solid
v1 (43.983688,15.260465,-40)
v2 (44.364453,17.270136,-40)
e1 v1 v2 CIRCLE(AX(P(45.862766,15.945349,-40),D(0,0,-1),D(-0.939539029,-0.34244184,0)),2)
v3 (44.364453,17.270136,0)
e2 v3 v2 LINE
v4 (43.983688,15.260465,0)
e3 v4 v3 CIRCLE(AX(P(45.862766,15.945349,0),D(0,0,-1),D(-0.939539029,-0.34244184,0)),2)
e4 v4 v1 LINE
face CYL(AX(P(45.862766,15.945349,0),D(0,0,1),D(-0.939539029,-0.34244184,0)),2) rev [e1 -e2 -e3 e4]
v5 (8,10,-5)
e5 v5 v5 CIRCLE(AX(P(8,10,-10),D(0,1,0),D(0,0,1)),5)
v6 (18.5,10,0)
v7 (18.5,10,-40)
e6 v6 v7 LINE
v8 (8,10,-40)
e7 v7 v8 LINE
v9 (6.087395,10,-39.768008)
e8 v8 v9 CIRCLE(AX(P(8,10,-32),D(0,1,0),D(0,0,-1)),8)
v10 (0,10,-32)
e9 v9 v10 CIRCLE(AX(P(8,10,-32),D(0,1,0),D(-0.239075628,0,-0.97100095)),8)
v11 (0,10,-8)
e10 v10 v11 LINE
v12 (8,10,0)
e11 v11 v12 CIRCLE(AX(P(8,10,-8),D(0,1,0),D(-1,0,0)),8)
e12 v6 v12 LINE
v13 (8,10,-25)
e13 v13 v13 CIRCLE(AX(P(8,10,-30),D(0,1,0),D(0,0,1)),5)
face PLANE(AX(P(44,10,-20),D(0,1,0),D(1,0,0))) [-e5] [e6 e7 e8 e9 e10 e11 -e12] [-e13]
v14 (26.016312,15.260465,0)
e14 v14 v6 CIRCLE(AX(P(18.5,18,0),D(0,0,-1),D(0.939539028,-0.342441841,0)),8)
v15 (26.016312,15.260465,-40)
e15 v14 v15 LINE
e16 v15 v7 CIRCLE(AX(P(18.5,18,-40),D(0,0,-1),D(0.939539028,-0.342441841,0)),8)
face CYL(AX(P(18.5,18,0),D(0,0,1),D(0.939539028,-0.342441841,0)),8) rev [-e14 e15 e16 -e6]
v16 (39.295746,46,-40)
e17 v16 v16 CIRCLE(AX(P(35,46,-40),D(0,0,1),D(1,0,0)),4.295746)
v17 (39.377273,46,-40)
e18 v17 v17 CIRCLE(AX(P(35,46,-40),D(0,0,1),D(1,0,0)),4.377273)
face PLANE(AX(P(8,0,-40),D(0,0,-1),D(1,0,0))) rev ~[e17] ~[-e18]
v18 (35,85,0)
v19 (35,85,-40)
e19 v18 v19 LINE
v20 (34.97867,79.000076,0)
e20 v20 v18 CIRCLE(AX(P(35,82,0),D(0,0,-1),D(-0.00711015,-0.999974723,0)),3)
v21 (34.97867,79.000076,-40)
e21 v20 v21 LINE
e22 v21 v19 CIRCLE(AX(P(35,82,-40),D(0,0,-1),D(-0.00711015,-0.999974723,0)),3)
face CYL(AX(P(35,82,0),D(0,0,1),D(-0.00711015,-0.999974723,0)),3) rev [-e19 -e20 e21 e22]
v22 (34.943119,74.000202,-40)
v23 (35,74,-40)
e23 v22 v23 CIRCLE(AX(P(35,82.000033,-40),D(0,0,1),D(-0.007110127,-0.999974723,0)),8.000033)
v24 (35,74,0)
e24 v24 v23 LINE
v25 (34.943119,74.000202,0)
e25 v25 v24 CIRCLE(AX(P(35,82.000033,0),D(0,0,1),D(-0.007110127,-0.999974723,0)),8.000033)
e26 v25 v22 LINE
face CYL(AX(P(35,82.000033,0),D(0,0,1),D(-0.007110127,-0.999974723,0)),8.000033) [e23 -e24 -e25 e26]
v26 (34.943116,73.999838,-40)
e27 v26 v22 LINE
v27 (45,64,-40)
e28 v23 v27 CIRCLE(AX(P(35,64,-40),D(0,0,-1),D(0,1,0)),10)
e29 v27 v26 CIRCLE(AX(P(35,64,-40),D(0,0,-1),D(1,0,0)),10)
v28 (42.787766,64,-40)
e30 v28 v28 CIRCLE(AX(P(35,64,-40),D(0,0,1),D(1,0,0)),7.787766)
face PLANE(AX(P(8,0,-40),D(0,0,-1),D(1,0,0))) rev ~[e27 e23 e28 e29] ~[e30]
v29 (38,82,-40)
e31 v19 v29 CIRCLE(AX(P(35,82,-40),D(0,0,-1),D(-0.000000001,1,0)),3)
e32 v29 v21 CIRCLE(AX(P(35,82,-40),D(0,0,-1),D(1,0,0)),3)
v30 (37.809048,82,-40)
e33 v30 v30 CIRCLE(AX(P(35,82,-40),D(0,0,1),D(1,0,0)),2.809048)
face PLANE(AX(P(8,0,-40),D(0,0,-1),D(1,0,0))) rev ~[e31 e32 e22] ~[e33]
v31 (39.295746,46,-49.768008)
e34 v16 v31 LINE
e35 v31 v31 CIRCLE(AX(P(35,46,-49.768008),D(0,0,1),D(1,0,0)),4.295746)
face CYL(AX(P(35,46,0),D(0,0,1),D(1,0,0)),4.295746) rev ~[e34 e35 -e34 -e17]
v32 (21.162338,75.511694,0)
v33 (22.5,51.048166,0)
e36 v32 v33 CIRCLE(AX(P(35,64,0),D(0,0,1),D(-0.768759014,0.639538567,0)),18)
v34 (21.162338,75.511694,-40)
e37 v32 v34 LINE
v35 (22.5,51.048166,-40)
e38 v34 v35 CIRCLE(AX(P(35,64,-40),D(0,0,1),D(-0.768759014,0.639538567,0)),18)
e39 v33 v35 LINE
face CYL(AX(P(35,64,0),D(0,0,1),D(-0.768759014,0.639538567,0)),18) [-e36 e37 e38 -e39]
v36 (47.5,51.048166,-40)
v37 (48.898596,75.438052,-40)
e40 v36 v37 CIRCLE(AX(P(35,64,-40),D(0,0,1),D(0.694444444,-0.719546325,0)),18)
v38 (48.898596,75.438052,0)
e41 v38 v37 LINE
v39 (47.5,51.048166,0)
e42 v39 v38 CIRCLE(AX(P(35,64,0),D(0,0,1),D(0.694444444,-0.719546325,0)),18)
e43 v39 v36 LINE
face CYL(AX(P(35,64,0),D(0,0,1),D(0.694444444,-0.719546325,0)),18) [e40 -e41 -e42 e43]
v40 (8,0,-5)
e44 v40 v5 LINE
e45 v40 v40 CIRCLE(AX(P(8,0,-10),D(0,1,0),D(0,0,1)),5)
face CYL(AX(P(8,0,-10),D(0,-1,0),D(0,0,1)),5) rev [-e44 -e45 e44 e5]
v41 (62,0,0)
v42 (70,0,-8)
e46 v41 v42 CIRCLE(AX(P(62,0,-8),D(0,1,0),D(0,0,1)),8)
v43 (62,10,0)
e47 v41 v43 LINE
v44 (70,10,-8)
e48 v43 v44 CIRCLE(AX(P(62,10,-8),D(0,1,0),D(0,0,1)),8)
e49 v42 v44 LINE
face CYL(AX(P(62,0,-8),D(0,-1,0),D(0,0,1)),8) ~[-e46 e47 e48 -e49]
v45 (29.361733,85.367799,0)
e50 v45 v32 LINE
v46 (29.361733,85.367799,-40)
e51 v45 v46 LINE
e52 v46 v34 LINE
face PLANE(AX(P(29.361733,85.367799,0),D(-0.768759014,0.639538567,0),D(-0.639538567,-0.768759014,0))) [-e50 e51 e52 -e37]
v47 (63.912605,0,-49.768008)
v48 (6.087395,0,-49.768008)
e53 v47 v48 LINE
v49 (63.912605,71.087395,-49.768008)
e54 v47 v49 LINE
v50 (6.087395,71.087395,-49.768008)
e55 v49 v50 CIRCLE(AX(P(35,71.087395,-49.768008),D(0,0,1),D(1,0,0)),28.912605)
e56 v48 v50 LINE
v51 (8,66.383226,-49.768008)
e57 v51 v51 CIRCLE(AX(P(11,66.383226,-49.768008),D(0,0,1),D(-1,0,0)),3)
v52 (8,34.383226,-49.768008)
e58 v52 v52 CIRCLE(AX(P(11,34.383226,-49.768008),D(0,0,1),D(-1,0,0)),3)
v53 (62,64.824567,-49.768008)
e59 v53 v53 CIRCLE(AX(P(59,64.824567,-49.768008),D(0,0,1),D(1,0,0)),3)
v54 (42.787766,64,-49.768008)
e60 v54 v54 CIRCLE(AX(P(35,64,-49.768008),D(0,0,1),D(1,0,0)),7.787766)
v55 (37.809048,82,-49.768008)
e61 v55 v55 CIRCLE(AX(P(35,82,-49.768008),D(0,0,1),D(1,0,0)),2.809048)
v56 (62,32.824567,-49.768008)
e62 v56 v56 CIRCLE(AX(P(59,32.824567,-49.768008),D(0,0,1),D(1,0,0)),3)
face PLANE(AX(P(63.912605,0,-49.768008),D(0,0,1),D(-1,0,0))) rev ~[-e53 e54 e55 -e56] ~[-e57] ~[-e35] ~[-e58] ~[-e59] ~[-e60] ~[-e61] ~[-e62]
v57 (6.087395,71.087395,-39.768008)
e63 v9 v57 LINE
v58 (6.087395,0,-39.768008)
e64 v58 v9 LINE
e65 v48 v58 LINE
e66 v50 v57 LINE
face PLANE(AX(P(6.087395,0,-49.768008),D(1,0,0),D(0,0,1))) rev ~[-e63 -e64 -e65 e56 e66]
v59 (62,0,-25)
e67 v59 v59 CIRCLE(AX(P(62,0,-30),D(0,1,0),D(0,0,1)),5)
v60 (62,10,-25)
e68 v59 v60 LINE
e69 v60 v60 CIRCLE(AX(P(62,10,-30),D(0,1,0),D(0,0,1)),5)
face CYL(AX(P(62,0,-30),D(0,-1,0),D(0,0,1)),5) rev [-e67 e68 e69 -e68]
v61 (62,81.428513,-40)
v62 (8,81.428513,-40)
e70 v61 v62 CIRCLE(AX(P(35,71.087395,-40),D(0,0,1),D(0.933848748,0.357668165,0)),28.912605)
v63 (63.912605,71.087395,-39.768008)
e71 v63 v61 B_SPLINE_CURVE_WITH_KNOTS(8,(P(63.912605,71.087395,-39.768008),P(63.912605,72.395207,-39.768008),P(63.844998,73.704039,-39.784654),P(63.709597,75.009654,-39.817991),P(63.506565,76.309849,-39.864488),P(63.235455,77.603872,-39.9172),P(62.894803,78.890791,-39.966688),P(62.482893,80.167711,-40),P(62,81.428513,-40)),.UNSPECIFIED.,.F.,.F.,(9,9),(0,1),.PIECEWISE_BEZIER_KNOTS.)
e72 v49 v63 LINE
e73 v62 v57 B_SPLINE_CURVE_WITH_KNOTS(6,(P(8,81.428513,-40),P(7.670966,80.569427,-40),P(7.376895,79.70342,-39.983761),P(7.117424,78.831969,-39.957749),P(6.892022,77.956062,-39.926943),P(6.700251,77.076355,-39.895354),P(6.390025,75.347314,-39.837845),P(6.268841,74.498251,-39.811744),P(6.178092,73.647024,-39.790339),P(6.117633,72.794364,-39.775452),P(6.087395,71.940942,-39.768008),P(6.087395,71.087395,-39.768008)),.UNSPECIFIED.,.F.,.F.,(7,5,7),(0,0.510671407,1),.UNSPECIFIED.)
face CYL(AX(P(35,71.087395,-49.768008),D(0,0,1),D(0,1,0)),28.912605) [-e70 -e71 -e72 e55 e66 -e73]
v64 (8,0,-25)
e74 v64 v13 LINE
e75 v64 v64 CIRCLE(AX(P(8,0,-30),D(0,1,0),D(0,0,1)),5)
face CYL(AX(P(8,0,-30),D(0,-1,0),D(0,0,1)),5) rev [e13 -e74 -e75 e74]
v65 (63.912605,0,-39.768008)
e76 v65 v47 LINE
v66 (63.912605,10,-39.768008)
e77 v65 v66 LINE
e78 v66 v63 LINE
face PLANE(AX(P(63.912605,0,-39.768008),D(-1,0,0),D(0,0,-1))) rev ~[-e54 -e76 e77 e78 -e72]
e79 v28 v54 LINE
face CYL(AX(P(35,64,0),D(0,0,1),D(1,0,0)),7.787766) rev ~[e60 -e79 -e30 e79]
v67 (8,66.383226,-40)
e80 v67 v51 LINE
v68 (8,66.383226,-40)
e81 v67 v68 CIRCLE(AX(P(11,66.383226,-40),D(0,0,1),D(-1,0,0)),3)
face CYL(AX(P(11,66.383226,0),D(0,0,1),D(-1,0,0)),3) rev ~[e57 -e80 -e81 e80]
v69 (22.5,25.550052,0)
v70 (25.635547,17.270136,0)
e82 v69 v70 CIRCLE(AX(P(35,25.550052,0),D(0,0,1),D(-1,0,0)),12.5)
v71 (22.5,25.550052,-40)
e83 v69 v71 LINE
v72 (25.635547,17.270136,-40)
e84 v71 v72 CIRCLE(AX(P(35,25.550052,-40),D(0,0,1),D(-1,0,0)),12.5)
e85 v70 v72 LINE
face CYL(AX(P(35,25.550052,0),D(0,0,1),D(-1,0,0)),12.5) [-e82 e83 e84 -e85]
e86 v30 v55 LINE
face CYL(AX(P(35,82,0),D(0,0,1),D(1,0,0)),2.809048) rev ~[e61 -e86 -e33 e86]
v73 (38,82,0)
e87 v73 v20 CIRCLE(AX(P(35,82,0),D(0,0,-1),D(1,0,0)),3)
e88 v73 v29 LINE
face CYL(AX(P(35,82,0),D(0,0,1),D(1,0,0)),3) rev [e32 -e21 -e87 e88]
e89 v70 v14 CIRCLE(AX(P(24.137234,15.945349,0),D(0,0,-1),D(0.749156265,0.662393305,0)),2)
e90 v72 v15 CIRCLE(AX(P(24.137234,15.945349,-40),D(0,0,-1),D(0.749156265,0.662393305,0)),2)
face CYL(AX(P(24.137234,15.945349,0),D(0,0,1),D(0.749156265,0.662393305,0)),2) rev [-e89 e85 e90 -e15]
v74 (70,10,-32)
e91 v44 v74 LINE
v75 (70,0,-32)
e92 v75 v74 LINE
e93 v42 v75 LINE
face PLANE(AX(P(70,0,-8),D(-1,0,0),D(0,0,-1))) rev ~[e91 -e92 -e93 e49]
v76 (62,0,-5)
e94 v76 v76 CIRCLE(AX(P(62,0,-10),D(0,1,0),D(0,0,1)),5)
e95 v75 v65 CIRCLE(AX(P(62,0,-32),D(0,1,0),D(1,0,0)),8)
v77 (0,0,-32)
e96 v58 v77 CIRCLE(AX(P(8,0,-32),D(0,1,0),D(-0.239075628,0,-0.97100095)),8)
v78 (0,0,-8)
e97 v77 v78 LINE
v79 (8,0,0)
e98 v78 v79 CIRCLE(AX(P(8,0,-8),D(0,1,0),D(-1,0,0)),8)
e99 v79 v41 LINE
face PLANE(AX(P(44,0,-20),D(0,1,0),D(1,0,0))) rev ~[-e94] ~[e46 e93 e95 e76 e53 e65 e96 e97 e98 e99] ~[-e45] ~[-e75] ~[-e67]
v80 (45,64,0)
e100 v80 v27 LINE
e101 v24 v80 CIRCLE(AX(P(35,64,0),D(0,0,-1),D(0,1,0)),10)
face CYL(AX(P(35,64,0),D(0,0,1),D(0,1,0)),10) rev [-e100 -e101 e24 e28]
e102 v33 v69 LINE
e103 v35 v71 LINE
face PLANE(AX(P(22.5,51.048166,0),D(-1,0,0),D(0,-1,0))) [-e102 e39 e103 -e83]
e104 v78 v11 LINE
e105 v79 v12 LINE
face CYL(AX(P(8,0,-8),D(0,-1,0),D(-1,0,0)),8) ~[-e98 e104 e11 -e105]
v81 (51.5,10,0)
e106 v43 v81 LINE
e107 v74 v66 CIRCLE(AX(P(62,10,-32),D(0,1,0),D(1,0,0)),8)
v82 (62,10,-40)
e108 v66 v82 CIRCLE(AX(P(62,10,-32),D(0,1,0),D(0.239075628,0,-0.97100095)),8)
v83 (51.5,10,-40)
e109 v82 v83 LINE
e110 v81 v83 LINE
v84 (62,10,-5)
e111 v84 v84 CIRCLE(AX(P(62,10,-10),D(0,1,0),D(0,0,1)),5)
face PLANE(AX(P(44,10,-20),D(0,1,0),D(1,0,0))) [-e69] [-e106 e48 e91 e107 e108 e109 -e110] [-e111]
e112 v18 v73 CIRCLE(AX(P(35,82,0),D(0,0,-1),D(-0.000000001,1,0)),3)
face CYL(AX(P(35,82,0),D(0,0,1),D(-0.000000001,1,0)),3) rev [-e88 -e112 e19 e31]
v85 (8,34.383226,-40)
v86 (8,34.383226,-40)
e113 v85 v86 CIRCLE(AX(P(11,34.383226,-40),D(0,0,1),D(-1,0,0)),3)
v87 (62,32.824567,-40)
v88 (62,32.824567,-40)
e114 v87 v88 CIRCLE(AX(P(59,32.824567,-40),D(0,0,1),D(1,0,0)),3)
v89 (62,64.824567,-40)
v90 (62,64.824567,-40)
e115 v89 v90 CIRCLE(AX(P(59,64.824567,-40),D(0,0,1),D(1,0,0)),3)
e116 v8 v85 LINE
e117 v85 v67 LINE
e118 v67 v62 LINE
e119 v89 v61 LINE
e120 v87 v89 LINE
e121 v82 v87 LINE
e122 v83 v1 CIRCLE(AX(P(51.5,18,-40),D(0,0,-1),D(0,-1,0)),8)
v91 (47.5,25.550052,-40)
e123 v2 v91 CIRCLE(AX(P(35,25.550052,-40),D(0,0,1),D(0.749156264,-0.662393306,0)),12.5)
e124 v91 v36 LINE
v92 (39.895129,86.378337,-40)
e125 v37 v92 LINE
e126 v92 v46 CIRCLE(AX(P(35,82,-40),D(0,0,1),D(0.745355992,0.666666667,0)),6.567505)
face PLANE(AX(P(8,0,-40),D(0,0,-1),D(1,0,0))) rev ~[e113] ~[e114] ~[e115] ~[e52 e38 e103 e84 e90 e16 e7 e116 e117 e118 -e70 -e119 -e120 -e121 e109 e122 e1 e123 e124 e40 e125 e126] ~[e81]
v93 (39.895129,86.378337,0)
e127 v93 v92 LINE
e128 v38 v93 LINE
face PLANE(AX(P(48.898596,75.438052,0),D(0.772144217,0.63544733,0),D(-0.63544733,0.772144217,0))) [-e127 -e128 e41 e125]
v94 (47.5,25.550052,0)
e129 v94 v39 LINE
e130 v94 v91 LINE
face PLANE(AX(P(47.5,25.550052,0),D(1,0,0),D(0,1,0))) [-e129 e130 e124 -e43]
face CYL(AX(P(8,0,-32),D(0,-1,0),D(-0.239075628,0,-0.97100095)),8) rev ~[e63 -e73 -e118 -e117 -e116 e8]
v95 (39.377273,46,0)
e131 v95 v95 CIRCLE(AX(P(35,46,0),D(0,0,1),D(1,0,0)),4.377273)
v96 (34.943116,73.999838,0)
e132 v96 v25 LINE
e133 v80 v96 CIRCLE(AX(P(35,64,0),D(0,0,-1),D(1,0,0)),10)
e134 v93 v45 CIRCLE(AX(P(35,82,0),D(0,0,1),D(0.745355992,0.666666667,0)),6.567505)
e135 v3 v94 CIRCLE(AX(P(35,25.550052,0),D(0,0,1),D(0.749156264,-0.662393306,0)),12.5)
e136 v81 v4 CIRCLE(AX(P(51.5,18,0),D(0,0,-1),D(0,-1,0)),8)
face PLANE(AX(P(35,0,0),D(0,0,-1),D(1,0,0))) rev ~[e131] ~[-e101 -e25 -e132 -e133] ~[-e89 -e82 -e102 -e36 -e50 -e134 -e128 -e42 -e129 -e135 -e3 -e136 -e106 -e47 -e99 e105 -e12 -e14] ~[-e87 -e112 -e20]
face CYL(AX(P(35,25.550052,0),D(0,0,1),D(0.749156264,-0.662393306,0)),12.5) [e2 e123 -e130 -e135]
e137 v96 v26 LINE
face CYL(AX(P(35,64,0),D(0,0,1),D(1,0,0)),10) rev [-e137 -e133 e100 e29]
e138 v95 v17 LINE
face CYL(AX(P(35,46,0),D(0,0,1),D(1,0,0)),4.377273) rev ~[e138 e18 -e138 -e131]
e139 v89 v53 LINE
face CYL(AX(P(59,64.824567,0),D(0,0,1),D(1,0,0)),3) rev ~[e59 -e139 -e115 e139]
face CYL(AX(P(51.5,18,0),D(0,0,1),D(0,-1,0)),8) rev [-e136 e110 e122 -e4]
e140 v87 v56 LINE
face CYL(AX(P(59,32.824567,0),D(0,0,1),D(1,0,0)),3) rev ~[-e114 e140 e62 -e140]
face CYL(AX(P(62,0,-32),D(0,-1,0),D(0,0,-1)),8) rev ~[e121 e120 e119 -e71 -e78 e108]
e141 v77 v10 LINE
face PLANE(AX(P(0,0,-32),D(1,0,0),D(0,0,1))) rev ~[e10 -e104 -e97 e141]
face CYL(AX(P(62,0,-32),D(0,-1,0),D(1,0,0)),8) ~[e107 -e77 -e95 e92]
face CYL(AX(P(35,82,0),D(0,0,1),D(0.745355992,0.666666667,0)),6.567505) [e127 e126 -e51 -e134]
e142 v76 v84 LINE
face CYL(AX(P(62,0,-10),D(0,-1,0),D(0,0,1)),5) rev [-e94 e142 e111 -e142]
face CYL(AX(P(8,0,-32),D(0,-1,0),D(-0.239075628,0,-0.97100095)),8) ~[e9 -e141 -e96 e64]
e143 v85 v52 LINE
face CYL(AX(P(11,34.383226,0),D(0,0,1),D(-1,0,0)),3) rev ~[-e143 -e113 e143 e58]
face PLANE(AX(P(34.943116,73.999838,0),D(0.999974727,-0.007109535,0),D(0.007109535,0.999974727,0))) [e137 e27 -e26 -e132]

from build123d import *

# Parameters (mm, degrees)
BASE_PLATE_AND_COLUMN_SKETCH_R = 5
BASE_PLATE_AND_COLUMN_SKETCH_W = 18
BASE_PLATE_AND_COLUMN_SKETCH_H = 40
BASE_PLATE_DEPTH               = 10
FRONT_PROFILE_SKETCH_R         = 4.377272593
FRONT_PROFILE_BOSS_40MM_DEPTH  = 40
UPRIGHT_COLUMN_100MM_DEPTH     = 100
COLUMN_EDGE_FILLETS_RADIUS     = 28.912605022
COLUMN_EDGE_FILLETS_LENGTH     = 10
SKETCH2_6_R                    = 4.295746386
SKETCH2_6_R_2                  = 7.787765557
SKETCH2_6_R_3                  = 2.809047726
THROUGH_CUT_A_DEPTH            = 100
SKETCH2_7_R                    = 3
THROUGH_CUT_B_DEPTH            = 100


with BuildPart() as part:
    # Base Plate and Column Sketch → Base Plate (new body)
    # profile 1 of 4: a face of its own
    with BuildSketch(Plane(origin=(0, 0, 0), x_dir=(1, 0, 0), z_dir=(0, 1, 0))):
        with BuildLine():
            Line((53, 40), (53, 0))
            Line((53, 0), (62, 0))
            ThreePointArc((62, 0), (67.656854249, 2.343145751), (70, 8))
            Line((70, 8), (70, 32))
            ThreePointArc((70, 32), (68.296857954, 36.934529351), (63.912605022, 39.768007597))
            ThreePointArc((63.912605022, 39.768007597), (62.963311793, 39.941790125), (62, 40))
            Line((62, 40), (53, 40))
        make_face()
        with Locations(Location((62, 10, 0), (0, 0, 270))):
            Circle(BASE_PLATE_AND_COLUMN_SKETCH_R, mode=Mode.SUBTRACT)
        with Locations(Location((62, 30, 0), (0, 0, 270))):
            Circle(BASE_PLATE_AND_COLUMN_SKETCH_R, mode=Mode.SUBTRACT)
    # profile 2 of 4: a face of its own
    with BuildSketch(Plane(origin=(0, 0, 0), x_dir=(1, 0, 0), z_dir=(0, 1, 0))):
        with BuildLine():
            ThreePointArc((0, 8), (2.343145751, 2.343145751), (8, 0))
            Line((8, 0), (17, 0))
            Line((17, 0), (17, 40))
            Line((17, 40), (8, 40))
            ThreePointArc((8, 40), (7.036688207, 39.941790125), (6.087394978, 39.768007597))
            ThreePointArc((6.087394978, 39.768007597), (1.703142046, 36.934529351), (0, 32))
            Line((0, 32), (0, 8))
        make_face()
        with Locations(Location((8, 10, 0), (0, 0, 270))):
            Circle(BASE_PLATE_AND_COLUMN_SKETCH_R, mode=Mode.SUBTRACT)
        with Locations(Location((8, 30, 0), (0, 0, 270))):
            Circle(BASE_PLATE_AND_COLUMN_SKETCH_R, mode=Mode.SUBTRACT)
    # profile 3 of 4: a face of its own
    with BuildSketch(Plane(origin=(0, 0, 0), x_dir=(1, 0, 0), z_dir=(0, 1, 0))):
        with Locations((26, 20)):
            Rectangle(BASE_PLATE_AND_COLUMN_SKETCH_W, BASE_PLATE_AND_COLUMN_SKETCH_H)
    # profile 4 of 4: a face of its own
    with BuildSketch(Plane(origin=(0, 0, 0), x_dir=(1, 0, 0), z_dir=(0, 1, 0))):
        with Locations((44, 20)):
            Rectangle(BASE_PLATE_AND_COLUMN_SKETCH_W, BASE_PLATE_AND_COLUMN_SKETCH_H)
    extrude(amount=BASE_PLATE_DEPTH)

    # Front Profile Sketch → Front Profile Boss 40mm (add)
    with BuildSketch(Plane.XY):
        with BuildLine():
            ThreePointArc((26.016312226, 15.260465273), (23.087140841, 11.445754131), (18.5, 10))
            Line((18.5, 10), (51.5, 10))
            ThreePointArc((51.5, 10), (46.912859159, 11.445754131), (43.983687774, 15.260465273))
            ThreePointArc((43.983687774, 15.260465273), (43.897725001, 16.317658687), (44.364453302, 17.270135567))
            ThreePointArc((44.364453302, 17.270135567), (46.68986027, 21.123183149), (47.5, 25.550051892))
            Line((47.5, 25.550051892), (47.5, 51.048166153))
            ThreePointArc((47.5, 51.048166153), (52.970478526, 62.969513929), (48.898595899, 75.438051934))
            Line((48.898595899, 75.438051934), (39.895129219, 86.378336678))
            ThreePointArc((39.895129219, 86.378336678), (34.372816044, 88.537489), (29.361733435, 85.367799323))
            Line((29.361733435, 85.367799323), (21.162337749, 75.511694203))
            ThreePointArc((21.162337749, 75.511694203), (17.026848791, 63.017230636), (22.5, 51.048166153))
            Line((22.5, 51.048166153), (22.5, 25.550051892))
            ThreePointArc((22.5, 25.550051892), (23.31013973, 21.123183149), (25.635546698, 17.270135567))
            ThreePointArc((25.635546698, 17.270135567), (26.102274999, 16.317658687), (26.016312226, 15.260465273))
        make_face()
        with Locations((35, 46)):
            Circle(FRONT_PROFILE_SKETCH_R, mode=Mode.SUBTRACT)
        with BuildLine():
            Line((34.943116214, 73.99983821), (34.943118802, 74.000202219))
            ThreePointArc((34.943118802, 74.000202219), (34.971559221, 74.000050555), (35, 74))
            ThreePointArc((35, 74), (42.071067812, 71.071067812), (45, 64))
            ThreePointArc((45, 64), (27.949072326, 56.908849252), (34.943116214, 73.99983821))
        make_face(mode=Mode.SUBTRACT)
        with BuildLine():
            ThreePointArc((38, 82), (37.113765438, 79.871151562), (34.978669551, 79.000075832))
            ThreePointArc((34.978669551, 79.000075832), (32.000018958, 82.010665292), (35, 85))
            ThreePointArc((35, 85), (37.121320344, 84.121320344), (38, 82))
        make_face(mode=Mode.SUBTRACT)
    extrude(amount=-FRONT_PROFILE_BOSS_40MM_DEPTH)

    # Sketch1_3 → Upright Column 100mm (add)
    with BuildSketch(Plane(origin=(0, 0, 0), x_dir=(1, 0, 0), z_dir=(0, 1, 0))):
        with BuildLine():
            Line((8, 40), (17, 40))
            Line((17, 40), (53, 40))
            Line((53, 40), (62, 40))
            ThreePointArc((62, 40), (62.963311793, 39.941790125), (63.912605022, 39.768007597))
            Line((63.912605022, 39.768007597), (63.912605022, 49.768007597))
            Line((63.912605022, 49.768007597), (6.087394978, 49.768007597))
            Line((6.087394978, 49.768007597), (6.087394978, 39.768007597))
            ThreePointArc((6.087394978, 39.768007597), (7.036688207, 39.941790125), (8, 40))
        make_face()
    extrude(amount=UPRIGHT_COLUMN_100MM_DEPTH)

    # Column Edge Fillets: full round fillet: the end face becomes a half cylinder, R = half its width
    column_edge_fillets_face = Plane((35, 100, -44.768007597), x_dir=(0, 0, 1), z_dir=(0, 1, 0))  # on the end face: x along it, z out of the body
    column_edge_fillets_slab = column_edge_fillets_face.offset(-COLUMN_EDGE_FILLETS_RADIUS / 2) * Box(COLUMN_EDGE_FILLETS_LENGTH, 2 * COLUMN_EDGE_FILLETS_RADIUS, COLUMN_EDGE_FILLETS_RADIUS, mode=Mode.PRIVATE)  # the body's end, R deep
    column_edge_fillets_round = Plane((35, 71.087394978, -44.768007597), x_dir=(0, 1, 0), z_dir=(0, 0, 1)) * Cylinder(COLUMN_EDGE_FILLETS_RADIUS, COLUMN_EDGE_FILLETS_LENGTH, mode=Mode.PRIVATE)  # its axis R under the face
    add(column_edge_fillets_slab - column_edge_fillets_round, mode=Mode.SUBTRACT)

    # Sketch2_6 → Through Cut A (cut)
    with BuildSketch(Plane.XY):
        with Locations((35, 46)):
            Circle(SKETCH2_6_R)
        with Locations((35, 64)):
            Circle(SKETCH2_6_R_2)
        with Locations((35, 82)):
            Circle(SKETCH2_6_R_3)
    extrude(amount=-THROUGH_CUT_A_DEPTH, mode=Mode.SUBTRACT)

    # Sketch2_7 → Through Cut B (cut)
    with BuildSketch(Plane.XY):
        with Locations((59, 64.824567346)):
            Circle(SKETCH2_7_R)
        with Locations((59, 32.824567346)):
            Circle(SKETCH2_7_R)
        with Locations(Location((11, 34.383225645, 0), (0, 0, 180))):
            Circle(SKETCH2_7_R)
        with Locations(Location((11, 66.383225645, 0), (0, 0, 180))):
            Circle(SKETCH2_7_R)
    extrude(amount=-THROUGH_CUT_B_DEPTH, mode=Mode.SUBTRACT)


solid = part.part
